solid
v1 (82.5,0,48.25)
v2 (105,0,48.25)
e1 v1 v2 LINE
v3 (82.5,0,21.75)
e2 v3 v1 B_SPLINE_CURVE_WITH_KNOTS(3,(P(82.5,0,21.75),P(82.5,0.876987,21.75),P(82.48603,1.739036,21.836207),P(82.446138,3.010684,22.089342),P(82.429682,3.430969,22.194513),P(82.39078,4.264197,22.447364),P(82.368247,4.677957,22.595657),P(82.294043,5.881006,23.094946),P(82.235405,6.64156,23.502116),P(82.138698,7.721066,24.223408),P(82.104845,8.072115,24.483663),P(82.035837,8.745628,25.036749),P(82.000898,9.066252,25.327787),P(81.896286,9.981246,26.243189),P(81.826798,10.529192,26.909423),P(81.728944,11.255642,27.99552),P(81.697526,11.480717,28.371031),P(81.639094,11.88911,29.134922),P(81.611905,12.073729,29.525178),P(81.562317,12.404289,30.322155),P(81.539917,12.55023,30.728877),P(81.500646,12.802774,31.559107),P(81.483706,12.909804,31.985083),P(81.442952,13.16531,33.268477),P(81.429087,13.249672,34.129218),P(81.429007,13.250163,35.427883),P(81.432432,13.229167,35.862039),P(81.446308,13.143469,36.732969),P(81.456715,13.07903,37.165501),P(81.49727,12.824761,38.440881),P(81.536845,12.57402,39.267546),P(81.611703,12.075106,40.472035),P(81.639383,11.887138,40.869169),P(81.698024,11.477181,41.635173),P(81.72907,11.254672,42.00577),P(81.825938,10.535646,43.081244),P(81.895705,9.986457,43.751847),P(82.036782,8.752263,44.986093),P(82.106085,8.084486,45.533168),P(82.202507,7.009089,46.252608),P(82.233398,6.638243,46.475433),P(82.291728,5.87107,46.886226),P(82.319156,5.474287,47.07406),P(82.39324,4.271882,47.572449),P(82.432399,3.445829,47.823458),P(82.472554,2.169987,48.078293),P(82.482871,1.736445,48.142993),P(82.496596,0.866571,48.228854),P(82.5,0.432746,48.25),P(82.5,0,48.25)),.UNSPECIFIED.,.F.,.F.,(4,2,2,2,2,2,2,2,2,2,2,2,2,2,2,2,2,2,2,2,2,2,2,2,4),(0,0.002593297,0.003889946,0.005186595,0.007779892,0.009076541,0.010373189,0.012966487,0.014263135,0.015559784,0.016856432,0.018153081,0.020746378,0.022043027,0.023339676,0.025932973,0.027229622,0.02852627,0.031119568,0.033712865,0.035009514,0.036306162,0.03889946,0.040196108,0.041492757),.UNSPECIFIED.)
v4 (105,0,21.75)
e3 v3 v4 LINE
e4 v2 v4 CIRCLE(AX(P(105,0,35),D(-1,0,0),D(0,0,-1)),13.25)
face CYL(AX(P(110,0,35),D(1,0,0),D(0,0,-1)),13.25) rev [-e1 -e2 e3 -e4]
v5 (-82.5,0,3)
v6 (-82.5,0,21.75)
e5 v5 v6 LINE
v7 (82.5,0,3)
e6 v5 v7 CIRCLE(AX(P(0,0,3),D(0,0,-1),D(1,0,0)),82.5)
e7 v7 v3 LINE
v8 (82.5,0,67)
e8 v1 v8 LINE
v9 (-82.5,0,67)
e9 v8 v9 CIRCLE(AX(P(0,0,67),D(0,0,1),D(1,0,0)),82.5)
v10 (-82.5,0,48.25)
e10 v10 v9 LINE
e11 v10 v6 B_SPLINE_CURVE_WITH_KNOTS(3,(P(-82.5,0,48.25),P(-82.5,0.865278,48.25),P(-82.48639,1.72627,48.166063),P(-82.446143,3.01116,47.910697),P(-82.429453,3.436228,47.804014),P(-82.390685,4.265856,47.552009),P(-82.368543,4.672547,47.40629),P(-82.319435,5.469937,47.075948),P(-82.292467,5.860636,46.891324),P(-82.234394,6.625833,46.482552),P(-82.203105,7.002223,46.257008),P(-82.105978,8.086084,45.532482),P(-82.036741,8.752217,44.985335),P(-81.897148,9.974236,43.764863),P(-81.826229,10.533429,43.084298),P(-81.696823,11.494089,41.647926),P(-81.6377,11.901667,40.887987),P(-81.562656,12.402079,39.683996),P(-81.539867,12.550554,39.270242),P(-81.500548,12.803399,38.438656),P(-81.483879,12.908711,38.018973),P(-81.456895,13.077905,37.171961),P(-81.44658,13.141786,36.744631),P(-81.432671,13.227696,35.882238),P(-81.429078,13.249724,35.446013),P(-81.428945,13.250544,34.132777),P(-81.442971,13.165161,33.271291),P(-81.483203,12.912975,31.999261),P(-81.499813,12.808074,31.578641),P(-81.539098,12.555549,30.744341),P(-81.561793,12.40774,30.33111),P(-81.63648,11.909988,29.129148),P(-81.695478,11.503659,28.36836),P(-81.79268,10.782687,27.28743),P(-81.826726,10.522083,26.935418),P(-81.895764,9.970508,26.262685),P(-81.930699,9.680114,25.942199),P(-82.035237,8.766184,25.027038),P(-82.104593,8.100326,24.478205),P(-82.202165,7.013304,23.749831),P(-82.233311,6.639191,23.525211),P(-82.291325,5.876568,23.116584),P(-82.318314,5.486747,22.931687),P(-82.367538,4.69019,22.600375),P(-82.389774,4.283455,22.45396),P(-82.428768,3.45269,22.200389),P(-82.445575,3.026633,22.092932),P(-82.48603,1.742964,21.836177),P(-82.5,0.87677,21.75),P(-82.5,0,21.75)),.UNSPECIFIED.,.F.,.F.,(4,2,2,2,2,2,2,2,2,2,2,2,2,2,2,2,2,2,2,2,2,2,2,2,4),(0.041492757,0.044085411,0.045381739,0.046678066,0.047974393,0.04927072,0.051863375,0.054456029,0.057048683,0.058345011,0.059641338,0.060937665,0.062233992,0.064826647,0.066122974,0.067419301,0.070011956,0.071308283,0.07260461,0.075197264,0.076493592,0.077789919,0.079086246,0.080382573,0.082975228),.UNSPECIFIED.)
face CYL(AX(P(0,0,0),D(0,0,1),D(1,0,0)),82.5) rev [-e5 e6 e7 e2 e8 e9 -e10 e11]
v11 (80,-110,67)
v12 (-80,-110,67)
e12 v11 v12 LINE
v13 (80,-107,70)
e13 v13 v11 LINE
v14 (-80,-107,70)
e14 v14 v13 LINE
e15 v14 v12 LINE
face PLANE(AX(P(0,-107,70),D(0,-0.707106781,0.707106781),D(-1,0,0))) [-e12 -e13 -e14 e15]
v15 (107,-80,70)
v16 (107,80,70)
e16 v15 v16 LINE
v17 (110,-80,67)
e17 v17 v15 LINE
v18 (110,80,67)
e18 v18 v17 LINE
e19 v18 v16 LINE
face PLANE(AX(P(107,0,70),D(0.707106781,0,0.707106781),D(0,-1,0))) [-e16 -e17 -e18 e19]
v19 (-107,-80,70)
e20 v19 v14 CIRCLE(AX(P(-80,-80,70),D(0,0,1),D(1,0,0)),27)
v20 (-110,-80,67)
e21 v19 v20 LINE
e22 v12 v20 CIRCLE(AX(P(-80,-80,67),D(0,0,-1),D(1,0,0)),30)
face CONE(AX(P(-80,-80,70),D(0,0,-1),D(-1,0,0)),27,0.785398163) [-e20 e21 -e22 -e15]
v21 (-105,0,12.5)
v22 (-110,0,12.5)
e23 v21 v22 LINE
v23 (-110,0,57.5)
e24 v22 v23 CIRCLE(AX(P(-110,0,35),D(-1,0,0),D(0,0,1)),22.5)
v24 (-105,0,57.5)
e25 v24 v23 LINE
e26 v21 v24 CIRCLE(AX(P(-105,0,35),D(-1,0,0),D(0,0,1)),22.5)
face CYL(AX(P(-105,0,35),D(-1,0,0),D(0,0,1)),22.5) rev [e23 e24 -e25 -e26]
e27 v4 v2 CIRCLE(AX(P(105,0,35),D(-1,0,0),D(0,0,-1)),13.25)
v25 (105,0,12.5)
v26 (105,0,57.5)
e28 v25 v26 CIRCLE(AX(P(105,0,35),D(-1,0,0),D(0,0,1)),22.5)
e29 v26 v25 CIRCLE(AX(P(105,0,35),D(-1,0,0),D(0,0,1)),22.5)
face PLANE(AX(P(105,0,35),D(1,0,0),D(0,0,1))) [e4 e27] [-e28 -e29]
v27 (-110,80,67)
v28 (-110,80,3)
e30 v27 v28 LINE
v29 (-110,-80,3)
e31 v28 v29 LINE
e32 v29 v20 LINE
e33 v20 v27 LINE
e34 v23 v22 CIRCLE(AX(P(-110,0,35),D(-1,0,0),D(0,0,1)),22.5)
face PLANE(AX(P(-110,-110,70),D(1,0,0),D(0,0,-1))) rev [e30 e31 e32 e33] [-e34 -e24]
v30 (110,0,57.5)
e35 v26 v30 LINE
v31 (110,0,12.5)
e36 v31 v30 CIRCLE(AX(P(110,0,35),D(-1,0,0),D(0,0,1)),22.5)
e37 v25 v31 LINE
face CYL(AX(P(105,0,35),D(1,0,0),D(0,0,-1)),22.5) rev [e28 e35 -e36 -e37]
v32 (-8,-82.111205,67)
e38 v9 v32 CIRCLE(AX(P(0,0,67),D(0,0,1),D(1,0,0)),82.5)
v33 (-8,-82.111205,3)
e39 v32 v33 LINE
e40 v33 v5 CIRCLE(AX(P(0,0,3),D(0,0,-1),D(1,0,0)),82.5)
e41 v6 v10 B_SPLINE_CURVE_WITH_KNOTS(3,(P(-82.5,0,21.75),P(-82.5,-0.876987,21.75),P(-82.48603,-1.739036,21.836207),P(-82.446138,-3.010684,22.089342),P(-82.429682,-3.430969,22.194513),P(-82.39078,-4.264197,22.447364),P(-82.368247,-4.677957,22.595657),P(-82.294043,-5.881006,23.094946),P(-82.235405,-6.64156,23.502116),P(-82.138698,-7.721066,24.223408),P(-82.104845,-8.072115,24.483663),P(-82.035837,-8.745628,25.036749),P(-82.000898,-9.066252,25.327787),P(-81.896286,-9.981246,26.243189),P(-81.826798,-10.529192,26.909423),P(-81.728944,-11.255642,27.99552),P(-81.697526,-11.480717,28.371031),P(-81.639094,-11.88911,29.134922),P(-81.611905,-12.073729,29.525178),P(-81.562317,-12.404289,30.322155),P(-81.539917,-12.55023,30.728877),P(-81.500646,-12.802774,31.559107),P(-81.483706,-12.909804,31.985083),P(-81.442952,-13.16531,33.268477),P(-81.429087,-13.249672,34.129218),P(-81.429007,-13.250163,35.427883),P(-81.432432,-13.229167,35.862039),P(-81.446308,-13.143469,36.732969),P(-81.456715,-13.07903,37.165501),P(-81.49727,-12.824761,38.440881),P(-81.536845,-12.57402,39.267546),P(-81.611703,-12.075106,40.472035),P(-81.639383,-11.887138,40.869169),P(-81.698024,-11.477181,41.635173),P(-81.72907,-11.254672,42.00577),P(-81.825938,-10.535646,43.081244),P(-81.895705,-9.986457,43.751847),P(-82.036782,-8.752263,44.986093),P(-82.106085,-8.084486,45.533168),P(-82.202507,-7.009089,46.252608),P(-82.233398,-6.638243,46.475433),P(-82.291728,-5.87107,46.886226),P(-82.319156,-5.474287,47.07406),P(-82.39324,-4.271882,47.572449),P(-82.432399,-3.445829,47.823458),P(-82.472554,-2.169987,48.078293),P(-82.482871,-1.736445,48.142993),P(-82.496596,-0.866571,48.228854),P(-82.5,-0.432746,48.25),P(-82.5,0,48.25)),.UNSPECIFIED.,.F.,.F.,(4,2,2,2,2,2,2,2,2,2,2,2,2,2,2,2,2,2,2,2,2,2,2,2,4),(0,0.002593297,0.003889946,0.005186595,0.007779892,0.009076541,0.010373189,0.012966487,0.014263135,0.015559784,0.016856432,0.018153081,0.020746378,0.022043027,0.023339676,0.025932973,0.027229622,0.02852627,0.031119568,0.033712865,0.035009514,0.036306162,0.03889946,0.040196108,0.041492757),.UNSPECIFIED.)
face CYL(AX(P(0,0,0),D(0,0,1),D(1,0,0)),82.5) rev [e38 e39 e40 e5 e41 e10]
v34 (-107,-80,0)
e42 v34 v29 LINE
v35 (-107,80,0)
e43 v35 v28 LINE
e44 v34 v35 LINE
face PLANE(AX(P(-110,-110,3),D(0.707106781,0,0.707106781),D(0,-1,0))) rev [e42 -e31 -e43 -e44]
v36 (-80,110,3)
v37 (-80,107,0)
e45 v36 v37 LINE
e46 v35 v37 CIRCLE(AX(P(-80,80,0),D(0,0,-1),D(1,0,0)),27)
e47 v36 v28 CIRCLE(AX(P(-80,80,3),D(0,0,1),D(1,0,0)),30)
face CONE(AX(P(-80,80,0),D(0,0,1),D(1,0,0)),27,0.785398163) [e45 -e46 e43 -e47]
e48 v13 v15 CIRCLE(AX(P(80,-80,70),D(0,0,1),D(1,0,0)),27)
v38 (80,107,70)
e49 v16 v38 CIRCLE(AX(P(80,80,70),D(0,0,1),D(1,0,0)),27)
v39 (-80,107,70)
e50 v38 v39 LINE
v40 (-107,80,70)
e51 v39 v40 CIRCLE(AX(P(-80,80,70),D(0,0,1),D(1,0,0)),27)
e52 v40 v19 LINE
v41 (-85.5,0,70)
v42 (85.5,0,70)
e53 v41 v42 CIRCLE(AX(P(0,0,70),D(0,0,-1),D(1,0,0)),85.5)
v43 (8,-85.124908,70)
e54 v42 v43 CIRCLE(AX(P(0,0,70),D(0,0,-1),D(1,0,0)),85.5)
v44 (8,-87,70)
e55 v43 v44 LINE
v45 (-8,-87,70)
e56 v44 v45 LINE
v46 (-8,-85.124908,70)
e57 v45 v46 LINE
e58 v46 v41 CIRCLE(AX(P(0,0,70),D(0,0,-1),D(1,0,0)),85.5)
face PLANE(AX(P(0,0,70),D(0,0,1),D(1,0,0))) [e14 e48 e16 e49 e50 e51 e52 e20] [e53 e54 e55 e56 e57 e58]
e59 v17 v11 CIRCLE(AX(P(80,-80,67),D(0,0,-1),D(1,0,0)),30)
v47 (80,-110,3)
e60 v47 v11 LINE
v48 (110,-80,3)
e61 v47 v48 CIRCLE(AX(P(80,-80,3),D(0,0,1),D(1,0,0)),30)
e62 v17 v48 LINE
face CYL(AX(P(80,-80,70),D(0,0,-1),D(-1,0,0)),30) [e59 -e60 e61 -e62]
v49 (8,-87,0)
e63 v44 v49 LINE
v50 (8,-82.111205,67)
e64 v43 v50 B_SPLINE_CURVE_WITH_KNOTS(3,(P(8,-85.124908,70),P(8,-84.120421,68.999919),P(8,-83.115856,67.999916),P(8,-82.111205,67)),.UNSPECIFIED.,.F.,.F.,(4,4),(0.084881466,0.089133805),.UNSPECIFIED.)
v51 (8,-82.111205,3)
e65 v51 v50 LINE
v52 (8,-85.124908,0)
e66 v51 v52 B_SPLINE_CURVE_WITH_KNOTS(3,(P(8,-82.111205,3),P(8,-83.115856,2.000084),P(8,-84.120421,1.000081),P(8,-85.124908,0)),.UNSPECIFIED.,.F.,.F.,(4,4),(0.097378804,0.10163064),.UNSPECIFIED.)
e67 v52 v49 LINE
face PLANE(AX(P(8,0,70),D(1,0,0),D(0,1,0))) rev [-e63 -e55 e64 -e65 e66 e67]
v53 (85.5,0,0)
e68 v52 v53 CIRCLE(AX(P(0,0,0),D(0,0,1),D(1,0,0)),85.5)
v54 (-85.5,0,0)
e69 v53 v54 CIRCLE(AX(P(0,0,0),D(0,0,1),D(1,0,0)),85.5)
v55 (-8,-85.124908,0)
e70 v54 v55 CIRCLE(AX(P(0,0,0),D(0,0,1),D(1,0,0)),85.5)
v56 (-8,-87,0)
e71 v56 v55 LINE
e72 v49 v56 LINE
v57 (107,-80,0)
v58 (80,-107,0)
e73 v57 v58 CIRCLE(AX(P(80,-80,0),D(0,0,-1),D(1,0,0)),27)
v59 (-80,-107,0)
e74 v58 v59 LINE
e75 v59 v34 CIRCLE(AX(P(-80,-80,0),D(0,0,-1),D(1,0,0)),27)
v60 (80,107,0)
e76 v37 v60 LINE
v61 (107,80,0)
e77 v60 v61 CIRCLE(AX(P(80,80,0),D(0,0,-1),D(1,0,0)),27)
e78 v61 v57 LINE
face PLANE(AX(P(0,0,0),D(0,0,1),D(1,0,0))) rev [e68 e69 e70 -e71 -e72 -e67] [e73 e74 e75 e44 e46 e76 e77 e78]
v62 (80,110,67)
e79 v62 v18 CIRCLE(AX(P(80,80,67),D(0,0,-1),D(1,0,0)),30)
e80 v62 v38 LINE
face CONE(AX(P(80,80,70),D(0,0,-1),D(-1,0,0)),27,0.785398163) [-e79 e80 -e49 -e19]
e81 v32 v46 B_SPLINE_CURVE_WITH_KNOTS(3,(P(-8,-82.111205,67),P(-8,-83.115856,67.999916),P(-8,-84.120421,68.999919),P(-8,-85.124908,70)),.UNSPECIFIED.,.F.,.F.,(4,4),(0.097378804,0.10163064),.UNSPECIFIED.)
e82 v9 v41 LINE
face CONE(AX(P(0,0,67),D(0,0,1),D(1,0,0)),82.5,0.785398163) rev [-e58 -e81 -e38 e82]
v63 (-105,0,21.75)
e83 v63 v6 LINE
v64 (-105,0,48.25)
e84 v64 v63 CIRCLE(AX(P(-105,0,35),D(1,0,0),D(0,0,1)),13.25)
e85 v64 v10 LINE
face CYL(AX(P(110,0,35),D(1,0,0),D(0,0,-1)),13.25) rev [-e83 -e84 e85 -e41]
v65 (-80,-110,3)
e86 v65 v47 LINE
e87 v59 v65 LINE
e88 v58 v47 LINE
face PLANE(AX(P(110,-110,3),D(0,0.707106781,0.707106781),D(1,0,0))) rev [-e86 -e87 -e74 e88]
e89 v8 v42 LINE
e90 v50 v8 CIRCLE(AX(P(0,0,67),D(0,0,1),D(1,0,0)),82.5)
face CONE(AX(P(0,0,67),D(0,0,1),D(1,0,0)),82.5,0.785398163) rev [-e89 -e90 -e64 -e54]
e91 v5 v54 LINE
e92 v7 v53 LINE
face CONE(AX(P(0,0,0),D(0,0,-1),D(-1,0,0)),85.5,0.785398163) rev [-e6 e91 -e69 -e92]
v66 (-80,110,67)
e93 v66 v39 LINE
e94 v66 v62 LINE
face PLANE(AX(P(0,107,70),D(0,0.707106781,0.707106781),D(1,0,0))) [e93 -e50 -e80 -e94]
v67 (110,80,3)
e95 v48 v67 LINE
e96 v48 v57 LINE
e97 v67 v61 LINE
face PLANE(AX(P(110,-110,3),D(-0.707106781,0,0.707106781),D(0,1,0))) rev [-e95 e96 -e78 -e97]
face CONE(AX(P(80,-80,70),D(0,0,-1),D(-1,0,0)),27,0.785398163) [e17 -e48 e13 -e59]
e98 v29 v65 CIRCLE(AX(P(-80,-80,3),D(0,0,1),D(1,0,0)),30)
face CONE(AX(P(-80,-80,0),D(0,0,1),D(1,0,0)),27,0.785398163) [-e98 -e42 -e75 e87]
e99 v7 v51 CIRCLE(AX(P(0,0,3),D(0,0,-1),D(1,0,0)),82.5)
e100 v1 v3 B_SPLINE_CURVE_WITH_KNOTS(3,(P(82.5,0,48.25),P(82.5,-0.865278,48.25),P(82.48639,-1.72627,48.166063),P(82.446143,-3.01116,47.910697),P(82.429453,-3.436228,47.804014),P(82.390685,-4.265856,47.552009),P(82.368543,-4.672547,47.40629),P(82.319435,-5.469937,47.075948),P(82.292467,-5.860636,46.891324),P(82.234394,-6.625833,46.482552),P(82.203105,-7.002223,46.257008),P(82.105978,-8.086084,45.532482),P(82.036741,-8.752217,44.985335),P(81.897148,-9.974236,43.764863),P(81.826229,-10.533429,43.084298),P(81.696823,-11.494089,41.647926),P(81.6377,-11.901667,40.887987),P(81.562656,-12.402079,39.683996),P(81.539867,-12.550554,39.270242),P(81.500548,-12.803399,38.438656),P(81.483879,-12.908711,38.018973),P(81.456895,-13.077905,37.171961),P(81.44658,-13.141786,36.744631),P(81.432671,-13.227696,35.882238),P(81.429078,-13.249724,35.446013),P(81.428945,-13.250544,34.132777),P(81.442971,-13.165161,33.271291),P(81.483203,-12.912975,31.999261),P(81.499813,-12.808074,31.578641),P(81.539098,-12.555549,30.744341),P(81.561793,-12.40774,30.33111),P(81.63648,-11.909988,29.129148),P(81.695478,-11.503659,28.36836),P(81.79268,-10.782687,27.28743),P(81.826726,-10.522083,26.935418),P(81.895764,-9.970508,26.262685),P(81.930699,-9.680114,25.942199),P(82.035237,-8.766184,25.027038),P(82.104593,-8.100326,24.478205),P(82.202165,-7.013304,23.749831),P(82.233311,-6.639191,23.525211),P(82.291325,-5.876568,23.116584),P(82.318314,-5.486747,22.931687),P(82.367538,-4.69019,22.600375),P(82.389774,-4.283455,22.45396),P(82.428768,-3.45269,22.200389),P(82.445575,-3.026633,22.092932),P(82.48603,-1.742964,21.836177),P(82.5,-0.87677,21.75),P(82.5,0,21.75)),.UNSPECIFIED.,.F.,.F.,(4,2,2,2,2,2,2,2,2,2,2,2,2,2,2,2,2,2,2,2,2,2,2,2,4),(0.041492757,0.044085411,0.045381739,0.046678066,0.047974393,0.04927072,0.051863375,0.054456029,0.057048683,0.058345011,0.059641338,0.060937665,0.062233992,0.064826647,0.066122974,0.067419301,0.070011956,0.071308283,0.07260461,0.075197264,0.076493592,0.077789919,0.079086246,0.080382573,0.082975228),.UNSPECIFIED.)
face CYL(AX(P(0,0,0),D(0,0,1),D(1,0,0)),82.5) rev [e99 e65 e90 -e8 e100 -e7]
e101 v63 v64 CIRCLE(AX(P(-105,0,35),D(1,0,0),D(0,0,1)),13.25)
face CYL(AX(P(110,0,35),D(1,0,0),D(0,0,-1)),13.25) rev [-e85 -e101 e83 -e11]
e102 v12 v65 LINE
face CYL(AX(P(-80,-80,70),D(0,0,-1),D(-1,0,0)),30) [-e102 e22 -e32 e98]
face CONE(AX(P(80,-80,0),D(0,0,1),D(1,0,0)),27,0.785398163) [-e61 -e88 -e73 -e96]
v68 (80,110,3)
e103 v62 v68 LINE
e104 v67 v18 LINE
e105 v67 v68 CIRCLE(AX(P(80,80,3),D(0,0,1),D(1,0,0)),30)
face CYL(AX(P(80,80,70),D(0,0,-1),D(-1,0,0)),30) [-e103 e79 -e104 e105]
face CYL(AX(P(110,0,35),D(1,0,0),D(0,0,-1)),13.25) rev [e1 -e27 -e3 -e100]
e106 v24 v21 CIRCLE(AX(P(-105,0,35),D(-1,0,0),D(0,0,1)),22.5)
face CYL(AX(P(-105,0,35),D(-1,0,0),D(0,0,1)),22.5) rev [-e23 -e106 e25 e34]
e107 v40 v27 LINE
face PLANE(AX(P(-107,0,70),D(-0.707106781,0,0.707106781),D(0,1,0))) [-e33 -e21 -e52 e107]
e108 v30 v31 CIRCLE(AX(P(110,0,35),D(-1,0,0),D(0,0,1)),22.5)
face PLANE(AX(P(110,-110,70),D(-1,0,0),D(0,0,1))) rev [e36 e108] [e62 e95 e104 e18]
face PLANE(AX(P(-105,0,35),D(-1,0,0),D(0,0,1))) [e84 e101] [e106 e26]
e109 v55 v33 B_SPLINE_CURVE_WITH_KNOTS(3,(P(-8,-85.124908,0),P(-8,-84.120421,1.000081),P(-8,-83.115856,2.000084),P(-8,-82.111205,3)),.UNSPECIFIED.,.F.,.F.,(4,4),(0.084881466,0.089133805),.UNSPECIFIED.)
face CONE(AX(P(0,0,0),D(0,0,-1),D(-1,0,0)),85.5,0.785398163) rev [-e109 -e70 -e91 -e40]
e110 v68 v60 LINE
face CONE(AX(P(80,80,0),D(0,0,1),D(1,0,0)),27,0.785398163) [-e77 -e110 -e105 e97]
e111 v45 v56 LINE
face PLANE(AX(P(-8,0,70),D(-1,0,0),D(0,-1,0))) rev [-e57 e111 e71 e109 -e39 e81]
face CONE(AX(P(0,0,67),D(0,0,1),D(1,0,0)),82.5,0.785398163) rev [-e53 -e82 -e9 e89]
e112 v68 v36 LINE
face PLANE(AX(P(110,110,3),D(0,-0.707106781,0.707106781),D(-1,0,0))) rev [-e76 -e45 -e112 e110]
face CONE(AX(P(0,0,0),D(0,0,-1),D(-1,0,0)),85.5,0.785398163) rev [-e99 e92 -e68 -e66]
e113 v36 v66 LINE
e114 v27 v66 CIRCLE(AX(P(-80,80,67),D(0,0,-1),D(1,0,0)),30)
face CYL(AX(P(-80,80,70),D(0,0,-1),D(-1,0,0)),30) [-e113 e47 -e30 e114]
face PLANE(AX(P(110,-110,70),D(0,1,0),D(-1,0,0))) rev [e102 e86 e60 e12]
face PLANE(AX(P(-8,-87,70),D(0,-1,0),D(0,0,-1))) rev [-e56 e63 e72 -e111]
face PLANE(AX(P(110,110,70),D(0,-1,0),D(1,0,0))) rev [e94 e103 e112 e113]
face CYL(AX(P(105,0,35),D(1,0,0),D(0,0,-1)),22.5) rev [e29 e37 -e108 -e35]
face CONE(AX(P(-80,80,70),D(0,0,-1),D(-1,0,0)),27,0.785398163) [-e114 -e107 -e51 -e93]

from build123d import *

# Parameters (mm, degrees)
SKETCH1_W           = 220
SKETCH1_H           = 220
BOSS_EXTRUDE1_DEPTH = 70
SKETCH2_R           = 82.5
CUT_EXTRUDE1_DEPTH  = 171.587221092
M30_TAPPED_HOLE1_D  = 26.5
SKETCH7_R           = 22.5
CUT_EXTRUDE3_DEPTH  = 5
FILLET1_R           = 30
CHAMFER1_SIZE       = 3
SKETCH8_W           = 16
SKETCH8_H           = 87
CUT_EXTRUDE4_DEPTH  = 171.587221092


with BuildPart() as part:
    # Sketch1 → Boss-Extrude1 (new body)
    with BuildSketch(Plane.XY):
        Rectangle(SKETCH1_W, SKETCH1_H)
    extrude(amount=BOSS_EXTRUDE1_DEPTH)

    # Sketch2 → Cut-Extrude1 (cut, through all)
    with BuildSketch(Plane.XY.offset(70)):
        Circle(SKETCH2_R)
    extrude(amount=-CUT_EXTRUDE1_DEPTH, mode=Mode.SUBTRACT)

    # M30 Tapped Hole1 (through all)
    with Locations(Plane(origin=(110, 0, 0), x_dir=(0, 0, -1), z_dir=(1, 0, 0))):
        with Locations((-35, 0)):
            Hole(M30_TAPPED_HOLE1_D / 2)

    # Sketch7 → Cut-Extrude3 (cut)
    with BuildSketch(Plane.ZY.offset(110)):
        with Locations((35, 0)):
            Circle(SKETCH7_R)
    cut_extrude3 = extrude(amount=-CUT_EXTRUDE3_DEPTH, mode=Mode.SUBTRACT)

    # Mirror1: Cut-Extrude3 across plane
    add(cut_extrude3.mirror(Plane(origin=(0, 0, 0), x_dir=(0, 0, 1), z_dir=(1, 0, 0))), mode=Mode.SUBTRACT)

    # Fillet1
    fillet1_edges = [part.edges().sort_by_distance(p)[0] for p in [
        (-110, 110, 35),
        (110, 110, 35),
        (110, -110, 35),
        (-110, -110, 35),
    ]]
    fillet(fillet1_edges, radius=FILLET1_R)

    # Chamfer1
    chamfer1_edges = [part.edges().sort_by_distance(p)[0] for p in [
        (-82.5, 0, 0),
        (-82.5, 0, 70),
        (0, 110, 0),
        (0, 110, 70),
        (-110, 0, 0),
        (110, 0, 0),
        (0, -110, 0),
        (-101.213203436, 101.213203436, 0),
        (-101.213203436, -101.213203436, 0),
        (101.213203436, -101.213203436, 0),
        (101.213203436, 101.213203436, 0),
        (110, 0, 70),
        (-110, 0, 70),
        (0, -110, 70),
        (-101.213203436, 101.213203436, 70),
        (-101.213203436, -101.213203436, 70),
        (101.213203436, -101.213203436, 70),
        (101.213203436, 101.213203436, 70),
    ]]
    chamfer(chamfer1_edges, length=CHAMFER1_SIZE)

    # Sketch8 → Cut-Extrude4 (cut, through all)
    with BuildSketch(Plane(origin=(0, 0, 0), x_dir=(-1, 0, 0), z_dir=(0, 0, -1))):
        with Locations((0, -43.5)):
            Rectangle(SKETCH8_W, SKETCH8_H)
    extrude(amount=-CUT_EXTRUDE4_DEPTH, mode=Mode.SUBTRACT)


solid = part.part
